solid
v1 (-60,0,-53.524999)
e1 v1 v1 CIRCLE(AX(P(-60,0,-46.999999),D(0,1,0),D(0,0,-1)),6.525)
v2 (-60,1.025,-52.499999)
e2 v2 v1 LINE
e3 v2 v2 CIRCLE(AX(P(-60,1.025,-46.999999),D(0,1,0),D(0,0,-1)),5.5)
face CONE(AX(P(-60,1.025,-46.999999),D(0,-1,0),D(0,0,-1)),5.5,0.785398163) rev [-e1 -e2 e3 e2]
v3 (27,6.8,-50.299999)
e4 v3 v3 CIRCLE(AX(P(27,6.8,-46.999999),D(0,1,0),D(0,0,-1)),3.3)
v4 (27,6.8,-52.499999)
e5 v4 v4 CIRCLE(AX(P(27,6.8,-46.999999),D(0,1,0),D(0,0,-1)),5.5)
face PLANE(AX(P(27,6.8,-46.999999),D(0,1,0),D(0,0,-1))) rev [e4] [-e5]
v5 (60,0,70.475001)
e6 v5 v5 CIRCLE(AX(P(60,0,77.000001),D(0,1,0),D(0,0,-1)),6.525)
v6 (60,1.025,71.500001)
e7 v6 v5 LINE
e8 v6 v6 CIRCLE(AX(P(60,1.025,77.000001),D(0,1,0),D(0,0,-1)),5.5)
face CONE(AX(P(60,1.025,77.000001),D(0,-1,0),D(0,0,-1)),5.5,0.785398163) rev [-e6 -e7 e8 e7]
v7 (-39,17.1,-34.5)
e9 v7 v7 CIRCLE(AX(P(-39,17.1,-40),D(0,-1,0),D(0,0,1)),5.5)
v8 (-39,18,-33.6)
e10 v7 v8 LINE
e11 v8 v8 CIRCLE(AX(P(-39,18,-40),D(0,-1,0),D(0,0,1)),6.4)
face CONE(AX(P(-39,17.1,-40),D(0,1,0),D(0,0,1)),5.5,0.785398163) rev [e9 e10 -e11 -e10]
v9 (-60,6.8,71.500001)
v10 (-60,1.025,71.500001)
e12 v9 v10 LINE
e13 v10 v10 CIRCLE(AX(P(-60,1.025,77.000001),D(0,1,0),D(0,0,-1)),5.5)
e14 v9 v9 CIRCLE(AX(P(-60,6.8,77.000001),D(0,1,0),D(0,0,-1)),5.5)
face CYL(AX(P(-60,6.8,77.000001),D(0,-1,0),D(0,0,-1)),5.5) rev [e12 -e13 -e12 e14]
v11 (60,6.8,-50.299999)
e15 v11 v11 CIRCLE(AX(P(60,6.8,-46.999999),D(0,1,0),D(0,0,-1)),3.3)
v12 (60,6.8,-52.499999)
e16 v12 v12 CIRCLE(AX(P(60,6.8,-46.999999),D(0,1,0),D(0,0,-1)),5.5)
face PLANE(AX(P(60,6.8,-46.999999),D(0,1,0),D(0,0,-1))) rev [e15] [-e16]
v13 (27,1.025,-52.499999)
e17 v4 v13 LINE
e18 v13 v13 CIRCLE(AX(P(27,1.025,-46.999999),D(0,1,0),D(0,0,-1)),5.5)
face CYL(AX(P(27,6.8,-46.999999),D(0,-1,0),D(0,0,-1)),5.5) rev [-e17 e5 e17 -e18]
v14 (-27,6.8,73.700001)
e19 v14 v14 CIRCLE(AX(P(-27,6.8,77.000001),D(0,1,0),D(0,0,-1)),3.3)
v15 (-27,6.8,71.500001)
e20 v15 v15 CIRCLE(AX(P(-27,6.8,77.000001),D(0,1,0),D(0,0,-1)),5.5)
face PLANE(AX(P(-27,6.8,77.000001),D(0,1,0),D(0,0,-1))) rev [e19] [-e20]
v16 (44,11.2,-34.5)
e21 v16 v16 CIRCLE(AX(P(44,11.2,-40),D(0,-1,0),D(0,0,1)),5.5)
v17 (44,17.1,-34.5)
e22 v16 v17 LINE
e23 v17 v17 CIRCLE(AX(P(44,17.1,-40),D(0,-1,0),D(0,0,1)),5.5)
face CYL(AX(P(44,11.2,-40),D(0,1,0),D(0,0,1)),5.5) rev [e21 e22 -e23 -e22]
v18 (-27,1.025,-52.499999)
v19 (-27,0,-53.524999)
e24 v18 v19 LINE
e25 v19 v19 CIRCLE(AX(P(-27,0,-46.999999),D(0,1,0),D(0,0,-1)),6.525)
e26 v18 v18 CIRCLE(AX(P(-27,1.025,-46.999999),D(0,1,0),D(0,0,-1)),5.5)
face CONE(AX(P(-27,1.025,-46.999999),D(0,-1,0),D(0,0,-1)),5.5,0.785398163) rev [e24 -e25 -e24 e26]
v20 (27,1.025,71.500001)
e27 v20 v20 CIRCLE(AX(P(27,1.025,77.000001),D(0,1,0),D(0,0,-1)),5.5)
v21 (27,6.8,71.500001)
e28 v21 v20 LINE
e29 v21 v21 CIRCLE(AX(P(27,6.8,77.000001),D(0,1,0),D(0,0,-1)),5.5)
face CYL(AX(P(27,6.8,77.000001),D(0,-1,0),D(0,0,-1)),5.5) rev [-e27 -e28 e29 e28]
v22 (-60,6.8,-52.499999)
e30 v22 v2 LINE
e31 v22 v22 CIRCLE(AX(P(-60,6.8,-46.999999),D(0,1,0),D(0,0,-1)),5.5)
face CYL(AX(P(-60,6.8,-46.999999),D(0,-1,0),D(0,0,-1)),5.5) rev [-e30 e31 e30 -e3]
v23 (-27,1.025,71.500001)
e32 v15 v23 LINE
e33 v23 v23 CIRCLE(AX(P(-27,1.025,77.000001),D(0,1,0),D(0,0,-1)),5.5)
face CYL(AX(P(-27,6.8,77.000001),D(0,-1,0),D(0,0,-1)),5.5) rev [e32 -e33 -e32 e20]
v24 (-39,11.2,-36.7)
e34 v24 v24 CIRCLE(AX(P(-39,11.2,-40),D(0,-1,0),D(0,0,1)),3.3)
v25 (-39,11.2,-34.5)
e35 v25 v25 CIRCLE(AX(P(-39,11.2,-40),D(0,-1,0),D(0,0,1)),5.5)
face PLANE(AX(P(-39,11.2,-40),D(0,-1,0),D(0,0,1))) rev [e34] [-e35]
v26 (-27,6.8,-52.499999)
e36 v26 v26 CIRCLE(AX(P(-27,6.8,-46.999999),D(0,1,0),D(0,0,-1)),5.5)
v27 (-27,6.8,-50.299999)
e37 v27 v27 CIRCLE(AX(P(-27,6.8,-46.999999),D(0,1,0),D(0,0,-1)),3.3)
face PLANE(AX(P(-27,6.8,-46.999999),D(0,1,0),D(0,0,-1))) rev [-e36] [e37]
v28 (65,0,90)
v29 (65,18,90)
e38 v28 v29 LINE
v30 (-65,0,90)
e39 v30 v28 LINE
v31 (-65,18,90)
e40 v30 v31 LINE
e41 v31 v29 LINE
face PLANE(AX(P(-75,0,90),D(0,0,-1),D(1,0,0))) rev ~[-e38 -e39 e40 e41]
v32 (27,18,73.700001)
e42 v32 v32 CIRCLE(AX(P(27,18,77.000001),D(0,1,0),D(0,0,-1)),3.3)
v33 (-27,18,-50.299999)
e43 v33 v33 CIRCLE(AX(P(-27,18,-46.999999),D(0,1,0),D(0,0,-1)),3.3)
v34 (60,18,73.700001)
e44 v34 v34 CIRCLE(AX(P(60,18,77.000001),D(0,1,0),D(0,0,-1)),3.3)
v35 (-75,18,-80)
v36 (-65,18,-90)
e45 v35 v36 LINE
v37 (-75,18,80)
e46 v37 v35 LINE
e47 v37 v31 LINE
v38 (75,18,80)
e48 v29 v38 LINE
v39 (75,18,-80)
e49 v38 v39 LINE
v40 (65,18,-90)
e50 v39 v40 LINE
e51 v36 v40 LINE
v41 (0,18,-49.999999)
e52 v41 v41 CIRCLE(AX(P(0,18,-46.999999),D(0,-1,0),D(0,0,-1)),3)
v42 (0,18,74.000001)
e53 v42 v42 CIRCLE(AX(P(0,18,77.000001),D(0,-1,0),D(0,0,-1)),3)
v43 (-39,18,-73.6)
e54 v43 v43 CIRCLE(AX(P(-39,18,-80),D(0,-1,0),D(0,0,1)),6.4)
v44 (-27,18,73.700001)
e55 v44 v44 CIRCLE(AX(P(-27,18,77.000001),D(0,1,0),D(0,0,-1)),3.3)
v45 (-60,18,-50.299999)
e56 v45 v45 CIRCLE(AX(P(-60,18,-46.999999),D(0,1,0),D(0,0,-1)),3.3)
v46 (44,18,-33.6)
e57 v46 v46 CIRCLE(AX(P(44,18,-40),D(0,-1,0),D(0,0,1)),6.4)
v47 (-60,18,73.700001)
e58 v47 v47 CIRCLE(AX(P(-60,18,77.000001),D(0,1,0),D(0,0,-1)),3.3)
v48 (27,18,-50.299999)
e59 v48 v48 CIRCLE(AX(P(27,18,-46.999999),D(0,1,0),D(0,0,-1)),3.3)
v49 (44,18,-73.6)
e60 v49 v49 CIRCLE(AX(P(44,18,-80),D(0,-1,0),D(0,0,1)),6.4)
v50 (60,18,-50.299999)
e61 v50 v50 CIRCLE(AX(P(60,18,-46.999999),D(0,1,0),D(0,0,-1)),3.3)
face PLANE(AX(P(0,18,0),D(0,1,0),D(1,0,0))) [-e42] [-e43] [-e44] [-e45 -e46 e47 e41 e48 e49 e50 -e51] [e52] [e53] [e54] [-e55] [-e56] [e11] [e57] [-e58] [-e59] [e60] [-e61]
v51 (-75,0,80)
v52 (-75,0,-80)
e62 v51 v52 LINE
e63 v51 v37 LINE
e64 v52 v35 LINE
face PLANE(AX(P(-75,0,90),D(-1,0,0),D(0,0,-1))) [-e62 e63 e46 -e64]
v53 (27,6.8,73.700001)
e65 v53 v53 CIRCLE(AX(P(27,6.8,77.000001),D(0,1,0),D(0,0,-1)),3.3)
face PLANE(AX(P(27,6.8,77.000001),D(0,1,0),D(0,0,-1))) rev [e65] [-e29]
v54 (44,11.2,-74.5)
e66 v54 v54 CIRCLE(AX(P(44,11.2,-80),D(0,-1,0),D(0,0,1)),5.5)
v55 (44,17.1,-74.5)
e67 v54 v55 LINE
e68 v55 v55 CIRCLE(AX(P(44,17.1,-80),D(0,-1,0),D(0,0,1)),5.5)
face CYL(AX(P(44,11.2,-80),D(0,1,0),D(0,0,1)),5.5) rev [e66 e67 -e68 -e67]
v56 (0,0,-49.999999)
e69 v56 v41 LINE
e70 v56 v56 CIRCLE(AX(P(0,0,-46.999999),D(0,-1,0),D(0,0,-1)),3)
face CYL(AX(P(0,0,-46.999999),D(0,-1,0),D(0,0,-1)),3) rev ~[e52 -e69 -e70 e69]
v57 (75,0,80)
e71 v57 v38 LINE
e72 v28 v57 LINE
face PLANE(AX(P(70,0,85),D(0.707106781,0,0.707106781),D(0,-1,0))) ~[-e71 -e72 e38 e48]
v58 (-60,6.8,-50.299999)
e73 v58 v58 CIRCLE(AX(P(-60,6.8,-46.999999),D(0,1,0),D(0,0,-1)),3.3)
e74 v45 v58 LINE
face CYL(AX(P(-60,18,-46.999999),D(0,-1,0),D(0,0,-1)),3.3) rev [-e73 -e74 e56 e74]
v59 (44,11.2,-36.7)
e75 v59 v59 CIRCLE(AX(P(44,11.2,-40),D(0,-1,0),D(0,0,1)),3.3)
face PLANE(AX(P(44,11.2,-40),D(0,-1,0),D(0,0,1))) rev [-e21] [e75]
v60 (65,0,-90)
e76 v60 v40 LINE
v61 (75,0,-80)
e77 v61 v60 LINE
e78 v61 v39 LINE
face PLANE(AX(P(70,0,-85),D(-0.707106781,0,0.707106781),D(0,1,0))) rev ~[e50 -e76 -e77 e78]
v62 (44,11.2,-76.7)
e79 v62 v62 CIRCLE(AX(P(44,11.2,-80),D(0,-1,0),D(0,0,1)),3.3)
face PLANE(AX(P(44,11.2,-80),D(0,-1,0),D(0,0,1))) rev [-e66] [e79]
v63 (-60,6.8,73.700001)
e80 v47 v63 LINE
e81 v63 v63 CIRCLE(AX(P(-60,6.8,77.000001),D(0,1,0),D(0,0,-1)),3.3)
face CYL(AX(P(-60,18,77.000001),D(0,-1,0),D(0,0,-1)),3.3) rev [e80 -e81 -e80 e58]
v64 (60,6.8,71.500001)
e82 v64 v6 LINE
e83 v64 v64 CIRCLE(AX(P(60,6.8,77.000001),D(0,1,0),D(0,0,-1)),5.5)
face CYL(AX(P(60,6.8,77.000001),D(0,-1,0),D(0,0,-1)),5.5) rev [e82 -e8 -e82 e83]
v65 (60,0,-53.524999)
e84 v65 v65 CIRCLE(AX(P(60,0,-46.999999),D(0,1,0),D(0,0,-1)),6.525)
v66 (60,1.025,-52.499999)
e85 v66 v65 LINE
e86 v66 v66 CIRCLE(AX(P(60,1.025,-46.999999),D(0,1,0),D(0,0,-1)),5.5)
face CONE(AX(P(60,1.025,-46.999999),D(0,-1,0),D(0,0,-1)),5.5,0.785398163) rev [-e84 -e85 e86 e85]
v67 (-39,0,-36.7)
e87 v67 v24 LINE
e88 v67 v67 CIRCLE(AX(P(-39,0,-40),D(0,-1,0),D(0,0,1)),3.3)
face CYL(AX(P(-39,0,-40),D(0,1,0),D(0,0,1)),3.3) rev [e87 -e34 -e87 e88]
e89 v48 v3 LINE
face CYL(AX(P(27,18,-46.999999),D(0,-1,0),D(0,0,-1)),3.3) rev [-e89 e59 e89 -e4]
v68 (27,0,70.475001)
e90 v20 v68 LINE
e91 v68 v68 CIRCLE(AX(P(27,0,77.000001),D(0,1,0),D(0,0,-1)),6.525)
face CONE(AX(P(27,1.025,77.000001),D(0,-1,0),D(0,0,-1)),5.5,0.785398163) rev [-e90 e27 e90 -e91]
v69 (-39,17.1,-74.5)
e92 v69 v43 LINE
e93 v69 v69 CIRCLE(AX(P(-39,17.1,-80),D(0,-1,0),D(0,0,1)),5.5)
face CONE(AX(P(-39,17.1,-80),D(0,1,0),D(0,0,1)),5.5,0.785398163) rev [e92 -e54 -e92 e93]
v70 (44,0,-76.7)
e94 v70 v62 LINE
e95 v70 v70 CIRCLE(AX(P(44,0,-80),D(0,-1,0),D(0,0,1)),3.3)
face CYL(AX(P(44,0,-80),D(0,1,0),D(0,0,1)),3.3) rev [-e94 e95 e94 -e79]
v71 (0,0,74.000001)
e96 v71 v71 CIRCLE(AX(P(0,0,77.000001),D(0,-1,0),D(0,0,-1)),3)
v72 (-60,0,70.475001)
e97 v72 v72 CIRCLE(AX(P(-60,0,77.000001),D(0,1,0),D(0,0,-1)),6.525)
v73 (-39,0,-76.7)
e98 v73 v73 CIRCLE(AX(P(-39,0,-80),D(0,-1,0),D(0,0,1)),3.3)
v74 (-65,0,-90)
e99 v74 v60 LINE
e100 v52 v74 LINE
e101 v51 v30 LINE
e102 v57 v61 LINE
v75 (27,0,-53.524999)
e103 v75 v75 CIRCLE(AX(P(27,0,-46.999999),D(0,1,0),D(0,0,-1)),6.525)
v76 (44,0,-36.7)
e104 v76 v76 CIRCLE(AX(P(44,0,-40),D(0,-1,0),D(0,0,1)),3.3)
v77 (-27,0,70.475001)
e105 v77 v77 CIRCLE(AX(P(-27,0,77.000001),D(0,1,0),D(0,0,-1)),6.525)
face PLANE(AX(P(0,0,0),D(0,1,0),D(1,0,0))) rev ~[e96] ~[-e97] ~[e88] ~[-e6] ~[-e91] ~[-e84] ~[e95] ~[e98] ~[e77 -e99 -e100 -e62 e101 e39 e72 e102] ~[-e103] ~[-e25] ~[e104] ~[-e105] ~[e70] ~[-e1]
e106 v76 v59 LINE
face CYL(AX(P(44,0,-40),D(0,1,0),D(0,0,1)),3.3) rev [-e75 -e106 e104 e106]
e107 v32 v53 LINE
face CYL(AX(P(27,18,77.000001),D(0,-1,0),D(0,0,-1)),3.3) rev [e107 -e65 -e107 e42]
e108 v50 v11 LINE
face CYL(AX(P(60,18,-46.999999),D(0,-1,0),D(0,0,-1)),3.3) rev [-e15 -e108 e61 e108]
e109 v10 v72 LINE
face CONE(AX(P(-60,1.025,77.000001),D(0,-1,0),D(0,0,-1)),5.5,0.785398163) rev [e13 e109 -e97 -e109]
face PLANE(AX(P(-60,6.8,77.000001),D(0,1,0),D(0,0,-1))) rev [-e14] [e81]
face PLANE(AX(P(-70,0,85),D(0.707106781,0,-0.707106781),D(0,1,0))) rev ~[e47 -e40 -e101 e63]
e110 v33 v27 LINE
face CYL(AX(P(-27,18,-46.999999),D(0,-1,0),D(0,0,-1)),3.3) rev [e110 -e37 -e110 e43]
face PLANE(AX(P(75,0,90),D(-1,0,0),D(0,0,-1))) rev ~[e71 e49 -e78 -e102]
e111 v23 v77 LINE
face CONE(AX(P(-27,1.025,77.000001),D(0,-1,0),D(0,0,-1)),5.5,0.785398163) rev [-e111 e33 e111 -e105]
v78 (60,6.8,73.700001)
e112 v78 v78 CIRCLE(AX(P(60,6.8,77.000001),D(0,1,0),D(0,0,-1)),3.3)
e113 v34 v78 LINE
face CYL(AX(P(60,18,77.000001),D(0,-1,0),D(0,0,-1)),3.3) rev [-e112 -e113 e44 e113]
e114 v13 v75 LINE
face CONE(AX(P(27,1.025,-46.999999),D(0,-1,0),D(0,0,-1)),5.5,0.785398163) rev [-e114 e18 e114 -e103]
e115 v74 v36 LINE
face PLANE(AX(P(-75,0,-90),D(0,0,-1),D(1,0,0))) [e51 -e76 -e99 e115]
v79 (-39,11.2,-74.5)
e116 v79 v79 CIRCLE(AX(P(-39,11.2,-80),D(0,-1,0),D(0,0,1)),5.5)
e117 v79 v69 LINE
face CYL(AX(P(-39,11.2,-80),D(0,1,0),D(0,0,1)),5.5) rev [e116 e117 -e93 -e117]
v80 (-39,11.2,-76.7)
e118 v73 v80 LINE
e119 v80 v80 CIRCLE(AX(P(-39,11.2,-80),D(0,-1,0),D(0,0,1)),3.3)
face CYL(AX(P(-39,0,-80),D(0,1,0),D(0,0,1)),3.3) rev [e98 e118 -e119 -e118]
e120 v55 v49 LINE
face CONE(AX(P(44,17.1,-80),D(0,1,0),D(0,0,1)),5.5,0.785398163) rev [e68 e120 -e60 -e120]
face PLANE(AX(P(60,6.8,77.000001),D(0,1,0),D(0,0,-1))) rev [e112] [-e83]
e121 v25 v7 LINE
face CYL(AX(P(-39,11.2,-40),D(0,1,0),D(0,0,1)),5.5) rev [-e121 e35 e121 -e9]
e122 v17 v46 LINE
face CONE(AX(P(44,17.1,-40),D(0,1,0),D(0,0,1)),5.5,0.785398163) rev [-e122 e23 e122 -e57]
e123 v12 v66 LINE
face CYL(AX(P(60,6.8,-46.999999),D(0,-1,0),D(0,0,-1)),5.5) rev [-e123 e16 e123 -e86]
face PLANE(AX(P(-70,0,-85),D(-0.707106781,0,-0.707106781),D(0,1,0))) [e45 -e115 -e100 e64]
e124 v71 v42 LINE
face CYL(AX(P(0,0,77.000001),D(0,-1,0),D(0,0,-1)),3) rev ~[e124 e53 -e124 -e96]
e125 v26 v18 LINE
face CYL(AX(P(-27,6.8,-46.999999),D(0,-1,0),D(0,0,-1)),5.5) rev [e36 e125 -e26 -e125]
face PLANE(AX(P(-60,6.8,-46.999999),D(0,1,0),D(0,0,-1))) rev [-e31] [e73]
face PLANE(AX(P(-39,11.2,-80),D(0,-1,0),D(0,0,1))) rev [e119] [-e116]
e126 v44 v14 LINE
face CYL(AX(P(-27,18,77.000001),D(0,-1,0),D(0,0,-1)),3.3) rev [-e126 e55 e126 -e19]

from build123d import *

# Parameters (mm, degrees)
SKETCH_1_W               = 150
SKETCH_1_H               = 180
EXTRUDE_1_DEPTH          = 18
CHAMFER_1_SIZE           = 10
HOLE_WIZARD_1_AT_2_COUNT = 2
HOLE_WIZARD_1_AT_2_PITCH = 33
HOLE_WIZARD_1_AT_3_COUNT = 2
HOLE_WIZARD_1_AT_3_PITCH = 87
HOLE_WIZARD_1_AT_4_COUNT = 2
HOLE_WIZARD_1_AT_4_PITCH = 120
HOLE_WIZARD_1_AT_5_COUNT = 2
HOLE_WIZARD_1_AT_5_PITCH = 124
HOLE_WIZARD_1_AT_6_COUNT = 2
HOLE_WIZARD_1_AT_6_PITCH = 128.316016148
HOLE_WIZARD_1_AT_7_COUNT = 2
HOLE_WIZARD_1_AT_7_PITCH = 151.476070717
HOLE_WIZARD_1_AT_8_COUNT = 2
HOLE_WIZARD_1_AT_8_PITCH = 172.557236881
SKETCH_6_R               = 3
CUT_EXTRUDE_1_DEPTH      = 119.528477591
HOLE_WIZARD_2_AT_2_COUNT = 2
HOLE_WIZARD_2_AT_2_PITCH = 40
HOLE_WIZARD_2_AT_3_COUNT = 2
HOLE_WIZARD_2_AT_3_PITCH = 92.135769384
HOLE_WIZARD_2_AT_4_COUNT = 2
HOLE_WIZARD_2_AT_4_PITCH = 83


with BuildPart() as part:
    # 草图1 → 凸台-拉伸1 (new body)
    with BuildSketch(Plane(origin=(0, 0, 0), x_dir=(1, 0, 0), z_dir=(0, 1, 0))):
        Rectangle(SKETCH_1_W, SKETCH_1_H)
    extrude(amount=EXTRUDE_1_DEPTH)

    # 倒角1
    chamfer_1_edges = [part.edges().sort_by_distance(p)[0] for p in [
        (75, 9, 90),
        (-75, 9, 90),
        (-75, 9, -90),
        (75, 9, -90),
    ]]
    chamfer(chamfer_1_edges, length=CHAMFER_1_SIZE)

    # 草图5 → 打孔尺寸(%根据)内六角圆柱头螺钉的类型1 (revolve, cut)
    with BuildSketch(Plane(origin=(60, 0, -46.999999026), x_dir=(0, 0, -1), z_dir=(1, 0, 0))):
        Polygon((0, 0), (0, 18), (3.3, 18), (3.3, 6.8), (5.5, 6.8), (5.5, 1.025), (6.525, 0), align=None)
    hole_wizard_1 = revolve(axis=Axis((60, -6.35, -46.999999026), (0, 1, 0)), mode=Mode.SUBTRACT)

    # 打孔尺寸(%根据)内六角圆柱头螺钉的类型1 at 2: 打孔尺寸(%根据)内六角圆柱头螺钉的类型1 ×2
    with Locations(*[(-i * HOLE_WIZARD_1_AT_2_PITCH, 0, 0) for i in range(1, HOLE_WIZARD_1_AT_2_COUNT)]):
        add(hole_wizard_1, mode=Mode.SUBTRACT)

    # 打孔尺寸(%根据)内六角圆柱头螺钉的类型1 at 3: 打孔尺寸(%根据)内六角圆柱头螺钉的类型1 ×2
    with Locations(*[(-i * HOLE_WIZARD_1_AT_3_PITCH, 0, 0) for i in range(1, HOLE_WIZARD_1_AT_3_COUNT)]):
        add(hole_wizard_1, mode=Mode.SUBTRACT)

    # 打孔尺寸(%根据)内六角圆柱头螺钉的类型1 at 4: 打孔尺寸(%根据)内六角圆柱头螺钉的类型1 ×2
    with Locations(*[(-i * HOLE_WIZARD_1_AT_4_PITCH, 0, 0) for i in range(1, HOLE_WIZARD_1_AT_4_COUNT)]):
        add(hole_wizard_1, mode=Mode.SUBTRACT)

    # 打孔尺寸(%根据)内六角圆柱头螺钉的类型1 at 5: 打孔尺寸(%根据)内六角圆柱头螺钉的类型1 ×2
    with Locations(*[(0, 0, i * HOLE_WIZARD_1_AT_5_PITCH) for i in range(1, HOLE_WIZARD_1_AT_5_COUNT)]):
        add(hole_wizard_1, mode=Mode.SUBTRACT)

    # 打孔尺寸(%根据)内六角圆柱头螺钉的类型1 at 6: 打孔尺寸(%根据)内六角圆柱头螺钉的类型1 ×2
    with Locations(*[Vector(-0.25717756045339407, 0, 0.9663641665538105) * (i * HOLE_WIZARD_1_AT_6_PITCH) for i in range(1, HOLE_WIZARD_1_AT_6_COUNT)]):
        add(hole_wizard_1, mode=Mode.SUBTRACT)

    # 打孔尺寸(%根据)内六角圆柱头螺钉的类型1 at 7: 打孔尺寸(%根据)内六角圆柱头螺钉的类型1 ×2
    with Locations(*[Vector(-0.5743481434915226, 0, 0.8186111470459227) * (i * HOLE_WIZARD_1_AT_7_PITCH) for i in range(1, HOLE_WIZARD_1_AT_7_COUNT)]):
        add(hole_wizard_1, mode=Mode.SUBTRACT)

    # 打孔尺寸(%根据)内六角圆柱头螺钉的类型1 at 8: 打孔尺寸(%根据)内六角圆柱头螺钉的类型1 ×2
    with Locations(*[Vector(-0.6954214275158859, 0, 0.7186021417667552) * (i * HOLE_WIZARD_1_AT_8_PITCH) for i in range(1, HOLE_WIZARD_1_AT_8_COUNT)]):
        add(hole_wizard_1, mode=Mode.SUBTRACT)

    # 草图6 → 切除-拉伸1 (cut, through all)
    with BuildSketch(Plane.XZ):
        with Locations(Location((0, -46.999999026, 0), (0, 0, 270))):
            Circle(SKETCH_6_R)
        with Locations(Location((0, 77.000000974, 0), (0, 0, 270))):
            Circle(SKETCH_6_R)
    extrude(amount=-CUT_EXTRUDE_1_DEPTH, mode=Mode.SUBTRACT)

    # 草图8 → 打孔尺寸(%根据)内六角圆柱头螺钉的类型2 (revolve, cut)
    with BuildSketch(Plane(origin=(-39, 18, -40), x_dir=(0, 0, 1), z_dir=(1, 0, 0))):
        Polygon((0, 0), (0, 18), (3.3, 18), (3.3, 6.8), (5.5, 6.8), (5.5, 0.9), (6.4, 0), align=None)
    hole_wizard_2 = revolve(axis=Axis((-39, 24.35, -40), (0, -1, 0)), mode=Mode.SUBTRACT)

    # 打孔尺寸(%根据)内六角圆柱头螺钉的类型2 at 2: 打孔尺寸(%根据)内六角圆柱头螺钉的类型2 ×2
    with Locations(*[(0, 0, -i * HOLE_WIZARD_2_AT_2_PITCH) for i in range(1, HOLE_WIZARD_2_AT_2_COUNT)]):
        add(hole_wizard_2, mode=Mode.SUBTRACT)

    # 打孔尺寸(%根据)内六角圆柱头螺钉的类型2 at 3: 打孔尺寸(%根据)内六角圆柱头螺钉的类型2 ×2
    with Locations(*[Vector(0.9008444880292467, 0, -0.4341419219418052) * (i * HOLE_WIZARD_2_AT_3_PITCH) for i in range(1, HOLE_WIZARD_2_AT_3_COUNT)]):
        add(hole_wizard_2, mode=Mode.SUBTRACT)

    # 打孔尺寸(%根据)内六角圆柱头螺钉的类型2 at 4: 打孔尺寸(%根据)内六角圆柱头螺钉的类型2 ×2
    with Locations(*[(i * HOLE_WIZARD_2_AT_4_PITCH, 0, 0) for i in range(1, HOLE_WIZARD_2_AT_4_COUNT)]):
        add(hole_wizard_2, mode=Mode.SUBTRACT)


solid = part.part
